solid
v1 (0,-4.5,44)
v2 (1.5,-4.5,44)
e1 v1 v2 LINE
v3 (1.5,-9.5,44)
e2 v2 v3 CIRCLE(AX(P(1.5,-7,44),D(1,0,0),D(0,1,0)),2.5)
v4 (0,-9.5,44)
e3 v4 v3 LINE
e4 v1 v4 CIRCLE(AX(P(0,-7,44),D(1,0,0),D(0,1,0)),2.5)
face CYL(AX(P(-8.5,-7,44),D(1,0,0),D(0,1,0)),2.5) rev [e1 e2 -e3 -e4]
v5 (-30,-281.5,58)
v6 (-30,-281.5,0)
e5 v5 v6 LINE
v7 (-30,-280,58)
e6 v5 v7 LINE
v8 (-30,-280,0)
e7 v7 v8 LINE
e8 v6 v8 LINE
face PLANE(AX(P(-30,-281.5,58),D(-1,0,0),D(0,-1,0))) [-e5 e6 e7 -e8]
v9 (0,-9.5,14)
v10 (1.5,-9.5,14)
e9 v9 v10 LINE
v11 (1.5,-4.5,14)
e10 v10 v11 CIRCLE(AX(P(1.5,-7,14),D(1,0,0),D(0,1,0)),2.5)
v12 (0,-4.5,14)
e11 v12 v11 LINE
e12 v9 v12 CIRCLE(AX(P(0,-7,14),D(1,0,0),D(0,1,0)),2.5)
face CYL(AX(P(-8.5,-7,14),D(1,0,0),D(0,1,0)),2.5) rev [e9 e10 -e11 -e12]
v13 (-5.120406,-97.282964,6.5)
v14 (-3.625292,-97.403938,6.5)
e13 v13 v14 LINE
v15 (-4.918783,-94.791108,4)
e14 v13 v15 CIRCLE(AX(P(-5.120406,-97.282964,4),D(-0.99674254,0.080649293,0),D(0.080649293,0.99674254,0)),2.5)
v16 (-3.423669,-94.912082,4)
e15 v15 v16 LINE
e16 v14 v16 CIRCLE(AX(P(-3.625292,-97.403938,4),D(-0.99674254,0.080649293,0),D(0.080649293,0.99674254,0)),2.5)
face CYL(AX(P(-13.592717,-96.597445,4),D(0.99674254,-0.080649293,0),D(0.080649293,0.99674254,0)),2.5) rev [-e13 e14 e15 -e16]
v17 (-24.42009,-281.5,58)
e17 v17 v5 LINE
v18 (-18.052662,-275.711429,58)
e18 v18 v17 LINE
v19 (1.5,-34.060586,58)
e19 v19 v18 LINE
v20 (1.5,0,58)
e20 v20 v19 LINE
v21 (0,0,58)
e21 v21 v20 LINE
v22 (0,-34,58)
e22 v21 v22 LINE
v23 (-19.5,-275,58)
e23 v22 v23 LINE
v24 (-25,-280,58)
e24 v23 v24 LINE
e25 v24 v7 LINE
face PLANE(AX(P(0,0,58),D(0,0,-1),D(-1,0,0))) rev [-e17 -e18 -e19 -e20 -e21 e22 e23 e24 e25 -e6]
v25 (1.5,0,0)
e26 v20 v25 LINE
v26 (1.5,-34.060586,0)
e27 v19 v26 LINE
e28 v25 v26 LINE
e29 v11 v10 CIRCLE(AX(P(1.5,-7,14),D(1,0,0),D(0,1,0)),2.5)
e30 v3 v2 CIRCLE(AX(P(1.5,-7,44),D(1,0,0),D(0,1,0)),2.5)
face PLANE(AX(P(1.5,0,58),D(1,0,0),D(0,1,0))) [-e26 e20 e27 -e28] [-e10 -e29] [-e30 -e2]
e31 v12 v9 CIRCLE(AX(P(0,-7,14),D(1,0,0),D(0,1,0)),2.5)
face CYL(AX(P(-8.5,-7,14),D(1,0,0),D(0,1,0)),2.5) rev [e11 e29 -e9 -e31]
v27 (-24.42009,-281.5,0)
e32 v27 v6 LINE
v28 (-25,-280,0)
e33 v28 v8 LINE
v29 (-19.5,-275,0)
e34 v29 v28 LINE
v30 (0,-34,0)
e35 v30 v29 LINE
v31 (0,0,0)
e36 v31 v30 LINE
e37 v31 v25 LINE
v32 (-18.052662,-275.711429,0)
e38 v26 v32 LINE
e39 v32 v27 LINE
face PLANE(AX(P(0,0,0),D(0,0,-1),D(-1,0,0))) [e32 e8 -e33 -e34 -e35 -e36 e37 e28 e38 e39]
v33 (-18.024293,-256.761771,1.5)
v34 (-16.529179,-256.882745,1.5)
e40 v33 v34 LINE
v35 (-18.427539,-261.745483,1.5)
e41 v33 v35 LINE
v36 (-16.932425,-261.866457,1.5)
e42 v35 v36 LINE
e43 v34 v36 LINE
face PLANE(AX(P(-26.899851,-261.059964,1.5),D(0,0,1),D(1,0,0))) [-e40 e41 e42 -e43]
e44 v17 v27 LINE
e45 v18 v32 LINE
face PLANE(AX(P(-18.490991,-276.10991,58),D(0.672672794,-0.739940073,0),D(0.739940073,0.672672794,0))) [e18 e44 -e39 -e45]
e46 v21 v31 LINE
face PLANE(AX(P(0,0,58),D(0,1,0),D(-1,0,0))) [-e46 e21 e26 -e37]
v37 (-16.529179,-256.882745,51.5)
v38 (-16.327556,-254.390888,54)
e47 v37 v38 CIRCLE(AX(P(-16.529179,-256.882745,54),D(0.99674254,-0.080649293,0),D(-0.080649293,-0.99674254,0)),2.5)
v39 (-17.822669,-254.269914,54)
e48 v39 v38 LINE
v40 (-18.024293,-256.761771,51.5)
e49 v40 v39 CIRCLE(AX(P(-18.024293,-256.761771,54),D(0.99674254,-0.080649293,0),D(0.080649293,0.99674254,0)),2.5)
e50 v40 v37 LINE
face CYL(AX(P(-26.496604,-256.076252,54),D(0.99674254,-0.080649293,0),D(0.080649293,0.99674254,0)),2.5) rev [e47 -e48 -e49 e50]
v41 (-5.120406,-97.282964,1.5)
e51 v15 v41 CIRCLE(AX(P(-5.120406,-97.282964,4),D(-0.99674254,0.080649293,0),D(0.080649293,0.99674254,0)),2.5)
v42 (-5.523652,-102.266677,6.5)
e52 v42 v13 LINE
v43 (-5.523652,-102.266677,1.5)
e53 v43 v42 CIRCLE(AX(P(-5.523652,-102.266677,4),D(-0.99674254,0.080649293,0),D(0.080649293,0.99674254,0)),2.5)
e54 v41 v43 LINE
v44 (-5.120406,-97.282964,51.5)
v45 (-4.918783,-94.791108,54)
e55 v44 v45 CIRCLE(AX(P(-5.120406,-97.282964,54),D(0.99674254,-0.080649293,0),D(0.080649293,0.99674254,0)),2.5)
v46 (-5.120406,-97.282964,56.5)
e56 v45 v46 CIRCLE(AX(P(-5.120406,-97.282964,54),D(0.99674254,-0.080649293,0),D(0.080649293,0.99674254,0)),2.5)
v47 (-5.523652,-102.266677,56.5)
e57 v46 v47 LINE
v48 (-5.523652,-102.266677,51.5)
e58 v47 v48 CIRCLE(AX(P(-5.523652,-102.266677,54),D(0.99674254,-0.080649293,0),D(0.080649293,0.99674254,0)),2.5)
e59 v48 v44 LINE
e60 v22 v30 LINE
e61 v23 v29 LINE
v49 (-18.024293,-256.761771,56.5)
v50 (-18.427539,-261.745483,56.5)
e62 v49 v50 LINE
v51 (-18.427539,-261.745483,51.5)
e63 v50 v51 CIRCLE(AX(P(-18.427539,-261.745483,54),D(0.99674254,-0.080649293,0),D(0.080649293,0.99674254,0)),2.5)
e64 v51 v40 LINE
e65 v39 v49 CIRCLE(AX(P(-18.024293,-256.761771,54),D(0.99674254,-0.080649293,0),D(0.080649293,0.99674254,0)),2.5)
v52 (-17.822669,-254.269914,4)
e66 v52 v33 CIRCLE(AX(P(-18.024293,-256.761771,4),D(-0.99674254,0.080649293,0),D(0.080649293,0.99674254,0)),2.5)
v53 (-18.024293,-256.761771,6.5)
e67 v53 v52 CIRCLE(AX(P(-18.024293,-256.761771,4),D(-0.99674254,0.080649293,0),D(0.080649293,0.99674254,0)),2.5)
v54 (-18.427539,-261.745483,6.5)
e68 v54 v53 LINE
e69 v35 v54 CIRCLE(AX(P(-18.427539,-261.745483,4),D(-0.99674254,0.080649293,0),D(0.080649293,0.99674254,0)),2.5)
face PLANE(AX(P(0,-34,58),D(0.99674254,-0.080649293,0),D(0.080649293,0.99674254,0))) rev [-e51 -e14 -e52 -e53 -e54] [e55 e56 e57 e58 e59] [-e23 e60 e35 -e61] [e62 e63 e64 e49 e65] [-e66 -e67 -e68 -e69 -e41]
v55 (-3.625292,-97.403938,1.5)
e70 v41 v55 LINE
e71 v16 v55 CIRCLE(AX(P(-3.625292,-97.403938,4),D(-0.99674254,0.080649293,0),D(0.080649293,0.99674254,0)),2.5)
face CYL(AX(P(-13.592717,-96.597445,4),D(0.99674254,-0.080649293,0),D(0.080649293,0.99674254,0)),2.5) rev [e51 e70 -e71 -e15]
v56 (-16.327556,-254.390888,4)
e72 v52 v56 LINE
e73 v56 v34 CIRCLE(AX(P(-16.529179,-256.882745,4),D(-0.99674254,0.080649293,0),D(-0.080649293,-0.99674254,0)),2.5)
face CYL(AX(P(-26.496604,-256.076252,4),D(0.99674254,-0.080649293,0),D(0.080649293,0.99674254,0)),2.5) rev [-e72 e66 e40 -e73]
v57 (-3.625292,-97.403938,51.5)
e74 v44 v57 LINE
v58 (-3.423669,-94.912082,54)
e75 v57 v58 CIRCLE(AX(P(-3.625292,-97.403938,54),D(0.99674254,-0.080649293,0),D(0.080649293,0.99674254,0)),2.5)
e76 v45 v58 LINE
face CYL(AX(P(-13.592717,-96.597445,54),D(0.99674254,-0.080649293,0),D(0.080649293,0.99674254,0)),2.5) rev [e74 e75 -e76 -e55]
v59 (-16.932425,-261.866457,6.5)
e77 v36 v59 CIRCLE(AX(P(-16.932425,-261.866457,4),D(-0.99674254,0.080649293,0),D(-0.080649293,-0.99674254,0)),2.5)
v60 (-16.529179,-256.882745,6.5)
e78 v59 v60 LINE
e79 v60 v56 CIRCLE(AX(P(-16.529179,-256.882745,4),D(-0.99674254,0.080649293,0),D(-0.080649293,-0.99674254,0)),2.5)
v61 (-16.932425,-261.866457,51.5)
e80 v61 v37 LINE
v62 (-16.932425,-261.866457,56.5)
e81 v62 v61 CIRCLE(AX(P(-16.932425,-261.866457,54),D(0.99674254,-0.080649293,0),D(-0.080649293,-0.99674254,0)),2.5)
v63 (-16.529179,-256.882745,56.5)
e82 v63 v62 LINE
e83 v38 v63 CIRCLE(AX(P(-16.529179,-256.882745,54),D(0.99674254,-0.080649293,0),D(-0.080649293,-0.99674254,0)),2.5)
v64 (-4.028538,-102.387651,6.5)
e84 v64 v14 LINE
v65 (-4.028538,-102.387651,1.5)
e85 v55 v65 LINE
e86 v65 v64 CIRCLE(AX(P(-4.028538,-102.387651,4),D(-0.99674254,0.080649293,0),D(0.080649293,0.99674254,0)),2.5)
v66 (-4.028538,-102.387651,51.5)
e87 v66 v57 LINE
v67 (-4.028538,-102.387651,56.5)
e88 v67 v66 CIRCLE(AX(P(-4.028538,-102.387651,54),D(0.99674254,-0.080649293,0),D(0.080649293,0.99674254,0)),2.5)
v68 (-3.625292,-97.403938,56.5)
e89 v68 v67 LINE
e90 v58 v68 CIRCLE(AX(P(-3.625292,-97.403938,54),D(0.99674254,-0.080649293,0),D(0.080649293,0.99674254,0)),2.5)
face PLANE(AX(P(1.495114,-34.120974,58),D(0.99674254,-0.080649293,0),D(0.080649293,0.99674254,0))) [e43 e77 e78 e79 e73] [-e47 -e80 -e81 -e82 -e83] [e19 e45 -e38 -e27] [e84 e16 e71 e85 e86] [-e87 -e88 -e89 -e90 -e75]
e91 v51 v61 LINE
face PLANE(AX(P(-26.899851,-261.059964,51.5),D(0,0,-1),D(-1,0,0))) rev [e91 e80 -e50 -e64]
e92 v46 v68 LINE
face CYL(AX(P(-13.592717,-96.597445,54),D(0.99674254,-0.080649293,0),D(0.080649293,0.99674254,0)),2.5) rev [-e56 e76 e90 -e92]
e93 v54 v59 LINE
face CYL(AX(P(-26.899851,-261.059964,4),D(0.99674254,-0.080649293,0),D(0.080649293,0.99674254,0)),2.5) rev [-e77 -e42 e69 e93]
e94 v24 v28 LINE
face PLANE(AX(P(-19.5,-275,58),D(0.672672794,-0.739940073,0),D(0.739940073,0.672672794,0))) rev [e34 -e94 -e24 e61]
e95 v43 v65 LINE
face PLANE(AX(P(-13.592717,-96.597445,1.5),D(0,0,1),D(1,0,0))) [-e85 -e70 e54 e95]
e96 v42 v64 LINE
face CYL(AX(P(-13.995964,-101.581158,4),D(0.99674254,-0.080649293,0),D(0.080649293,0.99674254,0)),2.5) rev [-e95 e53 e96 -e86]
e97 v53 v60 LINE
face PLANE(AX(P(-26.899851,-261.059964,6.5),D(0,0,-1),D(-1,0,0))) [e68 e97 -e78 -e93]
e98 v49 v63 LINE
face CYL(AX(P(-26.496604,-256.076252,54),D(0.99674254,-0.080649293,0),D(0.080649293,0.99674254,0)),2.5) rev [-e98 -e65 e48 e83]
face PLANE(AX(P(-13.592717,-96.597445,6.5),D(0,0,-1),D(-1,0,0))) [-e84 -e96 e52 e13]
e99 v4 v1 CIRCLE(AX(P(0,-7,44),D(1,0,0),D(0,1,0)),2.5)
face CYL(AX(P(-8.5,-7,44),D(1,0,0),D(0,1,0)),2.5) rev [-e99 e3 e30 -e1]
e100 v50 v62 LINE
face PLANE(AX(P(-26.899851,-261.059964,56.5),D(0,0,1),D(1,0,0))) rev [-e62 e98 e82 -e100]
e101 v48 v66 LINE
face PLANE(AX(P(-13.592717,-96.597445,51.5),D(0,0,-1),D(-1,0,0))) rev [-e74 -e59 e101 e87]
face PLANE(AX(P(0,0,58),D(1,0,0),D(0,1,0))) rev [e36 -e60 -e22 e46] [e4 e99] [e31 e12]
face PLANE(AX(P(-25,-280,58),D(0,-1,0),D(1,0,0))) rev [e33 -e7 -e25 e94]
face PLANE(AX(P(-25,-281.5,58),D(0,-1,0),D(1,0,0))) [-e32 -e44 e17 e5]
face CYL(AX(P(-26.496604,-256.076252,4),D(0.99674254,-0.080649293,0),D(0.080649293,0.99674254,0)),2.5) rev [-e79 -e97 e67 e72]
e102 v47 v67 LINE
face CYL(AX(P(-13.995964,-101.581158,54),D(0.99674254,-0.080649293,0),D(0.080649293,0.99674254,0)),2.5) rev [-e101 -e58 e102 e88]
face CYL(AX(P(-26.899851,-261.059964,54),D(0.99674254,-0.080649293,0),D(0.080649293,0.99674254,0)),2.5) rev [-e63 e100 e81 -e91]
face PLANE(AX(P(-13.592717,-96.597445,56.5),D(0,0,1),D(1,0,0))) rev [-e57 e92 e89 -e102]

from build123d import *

# Parameters (mm, degrees)
EXTRUDE_THIN2_DEPTH = 58
SKETCH2_R           = 2.5
CUT_EXTRUDE1_DEPTH  = 10
CUT_EXTRUDE2_DEPTH  = 10


with BuildPart() as part:
    # Sketch1 → Extrude-Thin2 (new body)
    with BuildSketch(Plane.XY):
        Polygon((0, 0), (0, -34), (-19.5, -275), (-25, -280), (-30, -280), (-30, -281.5), (-24.420089688, -281.5), (-18.0526616, -275.711429011), (1.5, -34.060585647), (1.5, 0), align=None)
    extrude(amount=EXTRUDE_THIN2_DEPTH)

    # Sketch2 → Cut-Extrude1 (cut)
    with BuildSketch(Plane(origin=(1.5, 0, 0), x_dir=(0, 0, -1), z_dir=(1, 0, 0))):
        with Locations(Location((-14, -7, 0), (0, 0, 90))):
            Circle(SKETCH2_R)
        with Locations(Location((-44, -7, 0), (0, 0, 90))):
            Circle(SKETCH2_R)
    extrude(amount=-CUT_EXTRUDE1_DEPTH, mode=Mode.SUBTRACT)

    # Sketch3 → Cut-Extrude2 (cut)
    with BuildSketch(Plane(origin=(4.228257559, -0.342120425, 0), x_dir=(0, 0, -1), z_dir=(0.9967425402733565, -0.08064929267772025, 0))):
        with BuildLine():
            Line((-51.5, -97.379026061), (-51.5, -102.379026061))
            ThreePointArc((-51.5, -102.379026061), (-54, -104.879026061), (-56.5, -102.379026061))
            Line((-56.5, -102.379026061), (-56.5, -97.379026061))
            ThreePointArc((-56.5, -97.379026061), (-54, -94.879026061), (-51.5, -97.379026061))
        make_face()
        with BuildLine():
            Line((-51.5, -262.379026061), (-51.5, -257.379026061))
            ThreePointArc((-51.5, -257.379026061), (-54, -254.879026061), (-56.5, -257.379026061))
            Line((-56.5, -257.379026061), (-56.5, -262.379026061))
            ThreePointArc((-56.5, -262.379026061), (-54, -264.879026061), (-51.5, -262.379026061))
        make_face()
    cut_extrude2 = extrude(amount=-CUT_EXTRUDE2_DEPTH, mode=Mode.SUBTRACT)

    # Mirror1: Cut-Extrude2 across plane
    add(cut_extrude2.mirror(Plane.XY.offset(29)), mode=Mode.SUBTRACT)


solid = part.part
